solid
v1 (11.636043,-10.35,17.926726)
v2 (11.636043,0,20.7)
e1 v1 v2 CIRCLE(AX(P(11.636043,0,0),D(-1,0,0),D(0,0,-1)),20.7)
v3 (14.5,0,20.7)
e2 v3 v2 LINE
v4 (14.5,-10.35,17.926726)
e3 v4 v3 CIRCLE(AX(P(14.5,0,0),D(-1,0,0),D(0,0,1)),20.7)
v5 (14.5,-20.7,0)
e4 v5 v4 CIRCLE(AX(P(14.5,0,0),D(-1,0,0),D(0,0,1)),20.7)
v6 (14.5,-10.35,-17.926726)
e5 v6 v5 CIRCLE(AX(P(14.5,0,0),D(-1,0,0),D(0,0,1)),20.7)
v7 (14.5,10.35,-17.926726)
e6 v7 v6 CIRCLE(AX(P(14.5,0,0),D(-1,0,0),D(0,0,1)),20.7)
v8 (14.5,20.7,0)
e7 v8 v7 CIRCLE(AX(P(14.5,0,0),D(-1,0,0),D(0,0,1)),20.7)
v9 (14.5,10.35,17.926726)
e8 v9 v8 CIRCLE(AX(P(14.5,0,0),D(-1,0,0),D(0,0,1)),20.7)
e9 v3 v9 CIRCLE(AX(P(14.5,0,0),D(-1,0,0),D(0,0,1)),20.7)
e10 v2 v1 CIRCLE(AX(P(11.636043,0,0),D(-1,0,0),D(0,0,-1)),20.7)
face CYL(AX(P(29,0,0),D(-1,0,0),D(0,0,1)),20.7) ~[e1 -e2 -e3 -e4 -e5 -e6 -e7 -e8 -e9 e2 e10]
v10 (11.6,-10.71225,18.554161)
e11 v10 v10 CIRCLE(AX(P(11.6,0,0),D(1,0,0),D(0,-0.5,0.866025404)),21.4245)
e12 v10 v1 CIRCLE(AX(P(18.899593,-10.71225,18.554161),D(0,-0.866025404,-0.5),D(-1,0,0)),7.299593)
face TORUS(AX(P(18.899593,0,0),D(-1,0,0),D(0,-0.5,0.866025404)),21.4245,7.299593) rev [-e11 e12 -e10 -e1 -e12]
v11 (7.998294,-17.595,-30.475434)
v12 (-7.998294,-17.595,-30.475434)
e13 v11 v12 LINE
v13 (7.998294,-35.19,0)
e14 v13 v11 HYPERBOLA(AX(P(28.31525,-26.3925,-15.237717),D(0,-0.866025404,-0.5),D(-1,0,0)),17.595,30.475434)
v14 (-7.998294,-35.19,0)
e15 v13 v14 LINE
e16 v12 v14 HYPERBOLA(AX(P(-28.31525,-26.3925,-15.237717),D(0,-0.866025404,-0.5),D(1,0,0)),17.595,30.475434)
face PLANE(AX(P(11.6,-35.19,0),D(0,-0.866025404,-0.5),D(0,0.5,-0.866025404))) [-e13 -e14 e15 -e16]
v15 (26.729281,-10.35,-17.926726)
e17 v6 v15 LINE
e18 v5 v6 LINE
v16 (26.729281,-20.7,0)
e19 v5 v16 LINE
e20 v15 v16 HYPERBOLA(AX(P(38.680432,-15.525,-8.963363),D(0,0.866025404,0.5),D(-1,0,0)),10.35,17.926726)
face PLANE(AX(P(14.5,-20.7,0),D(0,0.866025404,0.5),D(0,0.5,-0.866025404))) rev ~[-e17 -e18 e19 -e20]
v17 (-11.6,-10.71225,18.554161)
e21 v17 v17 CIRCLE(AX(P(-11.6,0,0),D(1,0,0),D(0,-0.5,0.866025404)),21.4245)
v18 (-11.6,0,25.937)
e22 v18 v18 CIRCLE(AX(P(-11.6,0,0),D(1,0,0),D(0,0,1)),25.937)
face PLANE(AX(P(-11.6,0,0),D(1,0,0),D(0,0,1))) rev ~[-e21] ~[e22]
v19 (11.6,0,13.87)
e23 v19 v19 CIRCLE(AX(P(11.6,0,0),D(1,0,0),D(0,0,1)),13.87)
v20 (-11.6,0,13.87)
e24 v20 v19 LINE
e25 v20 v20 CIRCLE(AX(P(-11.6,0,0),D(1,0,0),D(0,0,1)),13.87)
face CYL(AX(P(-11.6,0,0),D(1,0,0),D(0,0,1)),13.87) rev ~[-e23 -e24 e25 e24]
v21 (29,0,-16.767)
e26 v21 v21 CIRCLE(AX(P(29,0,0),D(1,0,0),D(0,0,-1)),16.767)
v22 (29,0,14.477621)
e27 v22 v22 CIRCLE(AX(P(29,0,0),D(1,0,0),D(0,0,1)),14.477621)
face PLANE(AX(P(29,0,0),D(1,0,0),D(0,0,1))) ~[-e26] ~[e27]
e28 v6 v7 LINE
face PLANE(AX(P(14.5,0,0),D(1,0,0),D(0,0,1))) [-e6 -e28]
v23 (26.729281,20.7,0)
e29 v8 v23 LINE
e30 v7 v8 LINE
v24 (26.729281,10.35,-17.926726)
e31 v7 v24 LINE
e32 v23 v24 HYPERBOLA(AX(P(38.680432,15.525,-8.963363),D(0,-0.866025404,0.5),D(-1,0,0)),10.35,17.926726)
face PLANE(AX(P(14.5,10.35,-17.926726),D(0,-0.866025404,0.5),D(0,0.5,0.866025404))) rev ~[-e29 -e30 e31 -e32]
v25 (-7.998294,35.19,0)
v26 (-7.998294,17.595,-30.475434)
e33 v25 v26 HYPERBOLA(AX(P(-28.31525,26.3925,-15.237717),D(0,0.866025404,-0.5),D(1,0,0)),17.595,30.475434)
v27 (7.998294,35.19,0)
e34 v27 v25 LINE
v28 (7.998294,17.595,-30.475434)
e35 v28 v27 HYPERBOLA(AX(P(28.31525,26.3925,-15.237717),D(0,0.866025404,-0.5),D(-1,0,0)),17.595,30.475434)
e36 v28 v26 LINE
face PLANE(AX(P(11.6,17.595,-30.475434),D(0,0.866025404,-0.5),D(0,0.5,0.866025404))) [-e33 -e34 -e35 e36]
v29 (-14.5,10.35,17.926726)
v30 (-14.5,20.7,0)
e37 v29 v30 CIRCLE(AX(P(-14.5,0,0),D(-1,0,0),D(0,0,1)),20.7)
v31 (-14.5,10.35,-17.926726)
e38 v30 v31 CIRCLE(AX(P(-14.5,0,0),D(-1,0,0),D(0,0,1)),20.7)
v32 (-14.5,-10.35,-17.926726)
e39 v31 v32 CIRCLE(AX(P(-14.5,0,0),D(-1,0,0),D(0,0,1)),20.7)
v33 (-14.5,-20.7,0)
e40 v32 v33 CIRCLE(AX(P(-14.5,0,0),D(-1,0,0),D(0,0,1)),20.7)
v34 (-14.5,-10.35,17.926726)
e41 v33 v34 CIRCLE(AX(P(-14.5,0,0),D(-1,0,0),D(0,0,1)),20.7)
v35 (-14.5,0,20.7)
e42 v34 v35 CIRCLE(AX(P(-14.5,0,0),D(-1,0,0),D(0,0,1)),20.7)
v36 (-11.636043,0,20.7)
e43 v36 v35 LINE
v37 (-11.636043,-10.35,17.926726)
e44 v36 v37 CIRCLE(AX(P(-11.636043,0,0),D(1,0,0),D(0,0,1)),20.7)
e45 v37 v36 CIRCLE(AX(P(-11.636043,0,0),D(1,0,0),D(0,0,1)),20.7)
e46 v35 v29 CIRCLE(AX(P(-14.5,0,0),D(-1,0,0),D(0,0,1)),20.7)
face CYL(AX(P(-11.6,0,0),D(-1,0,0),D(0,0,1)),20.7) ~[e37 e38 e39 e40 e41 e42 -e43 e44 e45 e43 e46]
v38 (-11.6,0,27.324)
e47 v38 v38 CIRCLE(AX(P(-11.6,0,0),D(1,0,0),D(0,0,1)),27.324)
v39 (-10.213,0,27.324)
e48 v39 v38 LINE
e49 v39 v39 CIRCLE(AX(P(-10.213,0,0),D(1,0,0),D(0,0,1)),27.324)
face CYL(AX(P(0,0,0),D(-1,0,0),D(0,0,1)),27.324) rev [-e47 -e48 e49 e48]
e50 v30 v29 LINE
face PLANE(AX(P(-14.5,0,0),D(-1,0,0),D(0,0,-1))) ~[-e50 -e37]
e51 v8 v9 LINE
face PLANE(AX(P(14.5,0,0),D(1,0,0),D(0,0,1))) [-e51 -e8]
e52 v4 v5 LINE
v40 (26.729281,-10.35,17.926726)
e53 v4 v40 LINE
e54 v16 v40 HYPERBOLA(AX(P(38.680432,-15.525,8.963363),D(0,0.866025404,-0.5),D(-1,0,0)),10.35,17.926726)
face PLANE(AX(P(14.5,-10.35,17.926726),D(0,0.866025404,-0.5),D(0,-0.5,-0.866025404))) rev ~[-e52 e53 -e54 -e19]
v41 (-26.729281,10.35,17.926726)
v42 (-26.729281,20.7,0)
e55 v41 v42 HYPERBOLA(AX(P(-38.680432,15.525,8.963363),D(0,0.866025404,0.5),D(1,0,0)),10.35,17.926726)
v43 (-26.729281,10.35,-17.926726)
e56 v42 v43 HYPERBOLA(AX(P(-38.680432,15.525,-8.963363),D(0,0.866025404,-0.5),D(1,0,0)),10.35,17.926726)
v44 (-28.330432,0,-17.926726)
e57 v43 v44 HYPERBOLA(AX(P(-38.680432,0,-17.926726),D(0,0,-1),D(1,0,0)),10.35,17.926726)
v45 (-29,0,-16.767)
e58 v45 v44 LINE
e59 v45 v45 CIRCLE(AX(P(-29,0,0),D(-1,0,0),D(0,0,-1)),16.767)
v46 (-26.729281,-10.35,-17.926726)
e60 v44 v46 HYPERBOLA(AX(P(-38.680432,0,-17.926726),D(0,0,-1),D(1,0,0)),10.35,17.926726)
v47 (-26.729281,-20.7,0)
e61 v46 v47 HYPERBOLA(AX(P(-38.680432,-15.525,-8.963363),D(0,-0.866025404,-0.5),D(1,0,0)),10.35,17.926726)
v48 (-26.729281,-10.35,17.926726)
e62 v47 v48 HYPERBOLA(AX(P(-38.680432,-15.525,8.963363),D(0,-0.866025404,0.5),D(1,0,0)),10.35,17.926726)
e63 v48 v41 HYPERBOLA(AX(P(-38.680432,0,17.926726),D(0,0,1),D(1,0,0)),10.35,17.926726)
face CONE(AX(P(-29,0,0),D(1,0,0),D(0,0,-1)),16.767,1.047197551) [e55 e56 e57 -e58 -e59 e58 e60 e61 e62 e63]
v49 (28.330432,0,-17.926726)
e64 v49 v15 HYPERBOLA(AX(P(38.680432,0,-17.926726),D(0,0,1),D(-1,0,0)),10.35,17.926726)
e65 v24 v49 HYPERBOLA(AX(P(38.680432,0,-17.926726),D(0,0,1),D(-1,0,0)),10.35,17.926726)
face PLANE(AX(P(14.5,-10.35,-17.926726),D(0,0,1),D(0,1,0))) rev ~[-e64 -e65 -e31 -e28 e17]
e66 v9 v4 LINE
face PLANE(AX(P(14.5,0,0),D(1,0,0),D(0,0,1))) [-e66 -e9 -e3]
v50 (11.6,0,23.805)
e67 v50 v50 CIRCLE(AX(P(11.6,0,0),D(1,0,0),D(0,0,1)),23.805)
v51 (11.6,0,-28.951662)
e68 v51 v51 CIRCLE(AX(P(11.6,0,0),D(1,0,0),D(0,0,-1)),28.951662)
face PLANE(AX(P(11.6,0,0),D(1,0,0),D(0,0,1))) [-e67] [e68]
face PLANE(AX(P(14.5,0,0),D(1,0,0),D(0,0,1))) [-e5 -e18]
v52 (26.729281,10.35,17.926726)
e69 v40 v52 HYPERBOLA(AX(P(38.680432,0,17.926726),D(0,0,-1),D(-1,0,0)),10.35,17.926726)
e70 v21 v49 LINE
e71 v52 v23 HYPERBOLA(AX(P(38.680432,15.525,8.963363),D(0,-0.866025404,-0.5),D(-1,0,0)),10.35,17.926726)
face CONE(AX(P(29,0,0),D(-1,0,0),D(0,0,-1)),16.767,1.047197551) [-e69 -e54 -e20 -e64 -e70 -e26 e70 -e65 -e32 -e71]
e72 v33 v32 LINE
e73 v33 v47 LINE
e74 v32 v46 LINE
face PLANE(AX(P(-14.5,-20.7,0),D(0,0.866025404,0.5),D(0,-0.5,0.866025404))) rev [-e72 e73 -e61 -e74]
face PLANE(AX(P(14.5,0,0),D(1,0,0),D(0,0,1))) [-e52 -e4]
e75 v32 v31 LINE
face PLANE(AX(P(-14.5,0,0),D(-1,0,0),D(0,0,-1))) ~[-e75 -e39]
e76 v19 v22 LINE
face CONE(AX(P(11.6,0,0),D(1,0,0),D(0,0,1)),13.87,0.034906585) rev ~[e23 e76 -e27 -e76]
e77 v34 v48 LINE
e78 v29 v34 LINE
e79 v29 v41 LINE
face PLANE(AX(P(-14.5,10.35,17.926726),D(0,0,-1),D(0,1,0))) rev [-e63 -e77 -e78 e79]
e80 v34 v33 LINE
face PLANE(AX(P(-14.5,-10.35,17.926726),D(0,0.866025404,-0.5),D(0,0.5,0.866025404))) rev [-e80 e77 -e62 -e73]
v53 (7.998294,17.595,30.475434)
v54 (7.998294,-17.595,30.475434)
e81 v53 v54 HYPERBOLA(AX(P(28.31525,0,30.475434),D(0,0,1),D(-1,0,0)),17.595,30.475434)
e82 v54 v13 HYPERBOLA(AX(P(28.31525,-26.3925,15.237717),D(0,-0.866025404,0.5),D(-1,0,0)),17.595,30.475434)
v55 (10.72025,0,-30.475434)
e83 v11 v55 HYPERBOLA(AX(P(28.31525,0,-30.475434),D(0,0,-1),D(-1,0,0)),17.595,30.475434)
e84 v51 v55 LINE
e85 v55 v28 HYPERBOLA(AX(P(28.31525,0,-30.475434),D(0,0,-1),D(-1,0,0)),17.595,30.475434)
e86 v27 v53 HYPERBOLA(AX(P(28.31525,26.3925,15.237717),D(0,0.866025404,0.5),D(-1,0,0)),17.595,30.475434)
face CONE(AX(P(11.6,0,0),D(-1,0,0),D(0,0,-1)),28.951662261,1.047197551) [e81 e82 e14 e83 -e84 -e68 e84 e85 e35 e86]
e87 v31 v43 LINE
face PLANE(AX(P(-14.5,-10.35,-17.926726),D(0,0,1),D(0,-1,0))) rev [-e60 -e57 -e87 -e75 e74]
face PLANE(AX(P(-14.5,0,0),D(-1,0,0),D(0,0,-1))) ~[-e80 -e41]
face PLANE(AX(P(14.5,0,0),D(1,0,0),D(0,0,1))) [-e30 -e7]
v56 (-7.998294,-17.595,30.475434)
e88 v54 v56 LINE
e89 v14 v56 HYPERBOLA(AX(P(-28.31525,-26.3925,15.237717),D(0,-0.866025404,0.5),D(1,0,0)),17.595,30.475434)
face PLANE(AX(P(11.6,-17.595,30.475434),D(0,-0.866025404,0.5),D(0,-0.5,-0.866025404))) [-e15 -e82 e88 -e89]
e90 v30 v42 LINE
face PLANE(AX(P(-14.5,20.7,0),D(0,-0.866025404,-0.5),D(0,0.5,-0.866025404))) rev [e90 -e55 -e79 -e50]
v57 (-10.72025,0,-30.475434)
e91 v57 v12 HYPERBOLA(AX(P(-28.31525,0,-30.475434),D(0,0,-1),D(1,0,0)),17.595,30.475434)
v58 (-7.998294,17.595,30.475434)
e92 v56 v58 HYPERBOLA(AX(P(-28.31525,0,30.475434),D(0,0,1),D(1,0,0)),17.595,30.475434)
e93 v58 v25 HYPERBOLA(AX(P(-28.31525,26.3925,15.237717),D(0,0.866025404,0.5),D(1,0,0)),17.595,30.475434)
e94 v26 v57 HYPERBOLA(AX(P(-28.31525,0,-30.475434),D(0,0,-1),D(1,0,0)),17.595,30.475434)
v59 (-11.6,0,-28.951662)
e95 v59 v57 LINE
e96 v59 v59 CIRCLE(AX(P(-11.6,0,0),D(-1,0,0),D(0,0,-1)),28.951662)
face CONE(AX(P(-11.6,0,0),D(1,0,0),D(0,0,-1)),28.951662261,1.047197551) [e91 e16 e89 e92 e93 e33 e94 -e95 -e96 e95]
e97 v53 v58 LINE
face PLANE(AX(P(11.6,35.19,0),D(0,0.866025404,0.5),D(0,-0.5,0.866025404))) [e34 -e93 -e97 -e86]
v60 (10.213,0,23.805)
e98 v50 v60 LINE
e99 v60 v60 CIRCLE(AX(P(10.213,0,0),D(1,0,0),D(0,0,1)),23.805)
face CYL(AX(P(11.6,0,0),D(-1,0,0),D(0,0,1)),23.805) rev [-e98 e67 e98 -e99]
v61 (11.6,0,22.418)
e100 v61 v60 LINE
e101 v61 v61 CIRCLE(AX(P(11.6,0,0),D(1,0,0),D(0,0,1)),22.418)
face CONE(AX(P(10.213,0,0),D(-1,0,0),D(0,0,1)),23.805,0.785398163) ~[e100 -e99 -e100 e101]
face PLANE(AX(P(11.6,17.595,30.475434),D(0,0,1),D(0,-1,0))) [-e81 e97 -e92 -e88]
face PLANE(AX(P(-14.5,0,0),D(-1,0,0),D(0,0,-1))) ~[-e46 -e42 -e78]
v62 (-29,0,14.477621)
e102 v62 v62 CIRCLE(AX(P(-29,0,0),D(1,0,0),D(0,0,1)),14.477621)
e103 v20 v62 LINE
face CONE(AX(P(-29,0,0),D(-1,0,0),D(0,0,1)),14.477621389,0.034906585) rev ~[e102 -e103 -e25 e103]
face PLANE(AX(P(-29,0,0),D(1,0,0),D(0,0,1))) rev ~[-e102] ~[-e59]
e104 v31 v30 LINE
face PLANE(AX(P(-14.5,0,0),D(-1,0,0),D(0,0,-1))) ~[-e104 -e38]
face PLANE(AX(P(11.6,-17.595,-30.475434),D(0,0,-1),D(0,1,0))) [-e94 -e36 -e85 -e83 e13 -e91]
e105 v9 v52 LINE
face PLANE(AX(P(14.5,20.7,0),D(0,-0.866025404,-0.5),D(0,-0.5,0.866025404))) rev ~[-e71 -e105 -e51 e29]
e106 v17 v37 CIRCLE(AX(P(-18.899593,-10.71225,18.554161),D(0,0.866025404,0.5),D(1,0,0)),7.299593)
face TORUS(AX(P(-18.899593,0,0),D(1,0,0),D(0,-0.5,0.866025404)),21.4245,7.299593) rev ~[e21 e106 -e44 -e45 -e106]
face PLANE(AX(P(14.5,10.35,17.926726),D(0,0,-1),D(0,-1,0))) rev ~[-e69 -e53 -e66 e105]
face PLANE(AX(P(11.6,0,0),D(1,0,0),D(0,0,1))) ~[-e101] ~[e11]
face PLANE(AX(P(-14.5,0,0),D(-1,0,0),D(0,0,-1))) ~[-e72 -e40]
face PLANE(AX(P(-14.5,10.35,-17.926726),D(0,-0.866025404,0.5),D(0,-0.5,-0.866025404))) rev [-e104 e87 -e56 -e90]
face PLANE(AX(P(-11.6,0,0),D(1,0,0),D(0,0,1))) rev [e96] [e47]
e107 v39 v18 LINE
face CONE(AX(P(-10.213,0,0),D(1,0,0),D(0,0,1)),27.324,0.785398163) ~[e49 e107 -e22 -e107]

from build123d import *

# Parameters (mm, degrees)
CHAMFER_1_SIZE           = 1.387
CUT_EXTRUDE_START        = -14.5
SKETCH_4_R               = 23.805
CUT_EXTRUDE_1_DEPTH      = 14.5
SKETCH_5_OUTSIDE_W       = 135.604
SKETCH_5_OUTSIDE_H       = 135.604
SKETCH_5_OUTSIDE_R       = 16.767
CUT_EXTRUDE_2_DEPTH      = 11.6
CUT_EXTRUDE_2_DRAFT      = -60
SKETCH_8_R               = 38.709
CUT_EXTRUDE_3_DEPTH      = 65.226413569
SKETCH_10_OUTSIDE_W      = 119.53
SKETCH_10_OUTSIDE_H      = 128.96
SKETCH_10_OUTSIDE_R      = 28.951662261
CUT_EXTRUDE_4_DEPTH      = 10
CUT_EXTRUDE_4_DRAFT      = -60
MIRROR_7_COPY_1_SKETCH_W = 135.604
MIRROR_7_COPY_1_SKETCH_H = 135.604
MIRROR_7_COPY_1_SKETCH_R = 16.767
MIRROR_7_COPY_1_DEPTH    = 11.6
MIRROR_7_COPY_1_DRAFT    = -60
MIRROR_7_COPY_2_SKETCH_W = 119.53
MIRROR_7_COPY_2_SKETCH_H = 128.96
MIRROR_7_COPY_2_SKETCH_R = 28.951662261
MIRROR_7_COPY_2_DEPTH    = 10
MIRROR_7_COPY_2_DRAFT    = -60


with BuildPart() as part:
    # 草图1 → 旋转1 (revolve)
    with BuildSketch(Plane.XY, mode=Mode.PRIVATE) as revolve_1_sk:
        Polygon((29, 20.7), (11.6, 20.7), (11.6, 23.805), (0, 23.805), (0, 27.324), (-11.6, 27.324), (-11.6, 20.7), (-29, 20.7), (-29, 14.477621389), (-11.6, 13.87), (11.6, 13.87), (29, 14.477621389), align=None)
    revolve(revolve_1_sk.sketch.rotate(Axis((0, 0, 0), (1, 0, 0)), 90), axis=Axis((0, 0, 0), (1, 0, 0)))

    # 倒角1
    chamfer_1_edges = [part.edges().sort_by_distance(p)[0] for p in [
        (-11.6, 0, -27.324),
        (11.6, 0, -23.805),
    ]]
    chamfer(chamfer_1_edges, length=CHAMFER_1_SIZE)

    # 草图3 → 旋转2 (revolve)
    with BuildSketch(Plane.XY, mode=Mode.PRIVATE) as revolve_2_sk:
        Polygon((-11.6, 27.324), (-11.6, 35.19), (11.6, 35.19), (11.6, 23.805), (0, 23.805), (0, 27.324), align=None)
    revolve(revolve_2_sk.sketch.rotate(Axis((0, 0, 0), (1, 0, 0)), 90), axis=Axis((0, 0, 0), (1, 0, 0)))

    # 草图4 → 切除-拉伸1 (cut)
    with BuildSketch(Plane(origin=(29, 0, 0), x_dir=(0, 0, -1), z_dir=(1, 0, 0)).offset(CUT_EXTRUDE_START)):
        with Locations(Location((0, 0, 0), (0, 0, 180))):
            Circle(SKETCH_4_R)
        Polygon((0, 20.7), (-17.926725858, 10.35), (-17.926725858, -10.35), (0, -20.7), (17.926725858, -10.35), (17.926725858, 10.35), align=None, mode=Mode.SUBTRACT)
    cut_extrude_1 = extrude(amount=CUT_EXTRUDE_1_DEPTH, mode=Mode.SUBTRACT)


with BuildPart() as cut_extrude_2_tool:
    # 草图5 outside → 切除-拉伸2 (with draft: the straight prism first)
    with BuildSketch(Plane(origin=(29, 0, 0), x_dir=(0, 0, -1), z_dir=(1, 0, 0))):
        Rectangle(SKETCH_5_OUTSIDE_W, SKETCH_5_OUTSIDE_H)
        Circle(SKETCH_5_OUTSIDE_R, mode=Mode.SUBTRACT)
    extrude(amount=-CUT_EXTRUDE_2_DEPTH)
    # 切除-拉伸2: the draft: its side faces are tilted about the plane it starts from
    cut_extrude_2_sides = [cut_extrude_2_tool.faces().sort_by_distance(p)[0] for p in [
        (23.2, -67.802, 0),
        (23.2, 0, -67.802),
        (23.2, 67.802, 0),
        (23.2, 0, 67.802),
        (23.2, 0, 16.767),
    ]]
    draft(cut_extrude_2_sides, Plane(origin=(29, 0, 0), x_dir=(0, 0, -1), z_dir=(1, 0, 0)), CUT_EXTRUDE_2_DRAFT)


with BuildPart() as part_1:
    add(part.part)

    # 切除-拉伸2: cut by cut_extrude_2_tool
    add(cut_extrude_2_tool.part, mode=Mode.SUBTRACT)

    # 草图6 → 旋转3 (revolve)
    with BuildSketch(Plane.XY, mode=Mode.PRIVATE) as revolve_3_sk:
        with BuildLine():
            Line((18.899592609, 14.124907391), (11.6, 14.124907391))
            Line((11.6, 14.124907391), (11.6, 21.4245))
            ThreePointArc((11.6, 21.4245), (13.738001175, 16.262908566), (18.899592609, 14.124907391))
        make_face()
    revolve_3 = revolve(revolve_3_sk.sketch.rotate(Axis((0, 0, 0), (1, 0, 0)), 120), axis=Axis((0, 0, 0), (1, 0, 0)))

    # 草图8 → 切除-拉伸3 (cut, through all)
    with BuildSketch(Plane(origin=(11.6, 0, 0), x_dir=(0, 0, -1), z_dir=(1, 0, 0))):
        Circle(SKETCH_8_R)
        Polygon((0, 35.19), (-30.475433959, 17.595), (-30.475433959, -17.595), (0, -35.19), (30.475433959, -17.595), (30.475433959, 17.595), align=None, mode=Mode.SUBTRACT)
    extrude(amount=-CUT_EXTRUDE_3_DEPTH, mode=Mode.SUBTRACT)


with BuildPart() as cut_extrude_4_tool:
    # 草图10 outside → 切除-拉伸4 (with draft: the straight prism first)
    with BuildSketch(Plane(origin=(11.6, 0, 0), x_dir=(0, 0, -1), z_dir=(1, 0, 0))):
        Rectangle(SKETCH_10_OUTSIDE_W, SKETCH_10_OUTSIDE_H)
        Circle(SKETCH_10_OUTSIDE_R, mode=Mode.SUBTRACT)
    extrude(amount=-CUT_EXTRUDE_4_DEPTH)
    # 切除-拉伸4: the draft: its side faces are tilted about the plane it starts from
    cut_extrude_4_sides = [cut_extrude_4_tool.faces().sort_by_distance(p)[0] for p in [
        (6.6, -64.48, 0),
        (6.6, 0, -59.765),
        (6.6, 64.48, 0),
        (6.6, 0, 59.765),
        (6.6, 0, 28.951662261),
    ]]
    draft(cut_extrude_4_sides, Plane(origin=(11.6, 0, 0), x_dir=(0, 0, -1), z_dir=(1, 0, 0)), CUT_EXTRUDE_4_DRAFT)


with BuildPart() as part_2:
    add(part_1.part)

    # 切除-拉伸4: cut by cut_extrude_4_tool
    add(cut_extrude_4_tool.part, mode=Mode.SUBTRACT)

    # 镜向7: 切除-拉伸1, 旋转3 across plane
    add(cut_extrude_1.mirror(Plane(origin=(0, 0, 0), x_dir=(0, 0, 1), z_dir=(1, 0, 0))), mode=Mode.SUBTRACT)
    add(revolve_3.mirror(Plane(origin=(0, 0, 0), x_dir=(0, 0, 1), z_dir=(1, 0, 0))))


with BuildPart() as mirror_7_copy_1_tool:
    # 镜向7 copy 1 sketch → 镜向7 copy 1 (with draft: the straight prism first)
    with BuildSketch(Plane(origin=(-29, 0, 0), x_dir=(0, 0, -1), z_dir=(-1, 0, 0))):
        Rectangle(MIRROR_7_COPY_1_SKETCH_W, MIRROR_7_COPY_1_SKETCH_H)
        Circle(MIRROR_7_COPY_1_SKETCH_R, mode=Mode.SUBTRACT)
    extrude(amount=-MIRROR_7_COPY_1_DEPTH)
    # 镜向7 copy 1: the draft: its side faces are tilted about the plane it starts from
    mirror_7_copy_1_sides = [mirror_7_copy_1_tool.faces().sort_by_distance(p)[0] for p in [
        (-23.2, -67.802, 0),
        (-23.2, 0, -67.802),
        (-23.2, 67.802, 0),
        (-23.2, 0, 67.802),
        (-23.2, 0, 16.767),
    ]]
    draft(mirror_7_copy_1_sides, Plane(origin=(-29, 0, 0), x_dir=(0, 0, -1), z_dir=(-1, 0, 0)), MIRROR_7_COPY_1_DRAFT)


with BuildPart() as part_3:
    add(part_2.part)

    # 镜向7 copy 1: cut by mirror_7_copy_1_tool
    add(mirror_7_copy_1_tool.part, mode=Mode.SUBTRACT)


with BuildPart() as mirror_7_copy_2_tool:
    # 镜向7 copy 2 sketch → 镜向7 copy 2 (with draft: the straight prism first)
    with BuildSketch(Plane(origin=(-11.6, 0, 0), x_dir=(0, 0, -1), z_dir=(-1, 0, 0))):
        Rectangle(MIRROR_7_COPY_2_SKETCH_W, MIRROR_7_COPY_2_SKETCH_H)
        Circle(MIRROR_7_COPY_2_SKETCH_R, mode=Mode.SUBTRACT)
    extrude(amount=-MIRROR_7_COPY_2_DEPTH)
    # 镜向7 copy 2: the draft: its side faces are tilted about the plane it starts from
    mirror_7_copy_2_sides = [mirror_7_copy_2_tool.faces().sort_by_distance(p)[0] for p in [
        (-6.6, -64.48, 0),
        (-6.6, 0, -59.765),
        (-6.6, 64.48, 0),
        (-6.6, 0, 59.765),
        (-6.6, 0, 28.951662261),
    ]]
    draft(mirror_7_copy_2_sides, Plane(origin=(-11.6, 0, 0), x_dir=(0, 0, -1), z_dir=(-1, 0, 0)), MIRROR_7_COPY_2_DRAFT)


with BuildPart() as part_4:
    add(part_3.part)

    # 镜向7 copy 2: cut by mirror_7_copy_2_tool
    add(mirror_7_copy_2_tool.part, mode=Mode.SUBTRACT)


solid = part_4.part
